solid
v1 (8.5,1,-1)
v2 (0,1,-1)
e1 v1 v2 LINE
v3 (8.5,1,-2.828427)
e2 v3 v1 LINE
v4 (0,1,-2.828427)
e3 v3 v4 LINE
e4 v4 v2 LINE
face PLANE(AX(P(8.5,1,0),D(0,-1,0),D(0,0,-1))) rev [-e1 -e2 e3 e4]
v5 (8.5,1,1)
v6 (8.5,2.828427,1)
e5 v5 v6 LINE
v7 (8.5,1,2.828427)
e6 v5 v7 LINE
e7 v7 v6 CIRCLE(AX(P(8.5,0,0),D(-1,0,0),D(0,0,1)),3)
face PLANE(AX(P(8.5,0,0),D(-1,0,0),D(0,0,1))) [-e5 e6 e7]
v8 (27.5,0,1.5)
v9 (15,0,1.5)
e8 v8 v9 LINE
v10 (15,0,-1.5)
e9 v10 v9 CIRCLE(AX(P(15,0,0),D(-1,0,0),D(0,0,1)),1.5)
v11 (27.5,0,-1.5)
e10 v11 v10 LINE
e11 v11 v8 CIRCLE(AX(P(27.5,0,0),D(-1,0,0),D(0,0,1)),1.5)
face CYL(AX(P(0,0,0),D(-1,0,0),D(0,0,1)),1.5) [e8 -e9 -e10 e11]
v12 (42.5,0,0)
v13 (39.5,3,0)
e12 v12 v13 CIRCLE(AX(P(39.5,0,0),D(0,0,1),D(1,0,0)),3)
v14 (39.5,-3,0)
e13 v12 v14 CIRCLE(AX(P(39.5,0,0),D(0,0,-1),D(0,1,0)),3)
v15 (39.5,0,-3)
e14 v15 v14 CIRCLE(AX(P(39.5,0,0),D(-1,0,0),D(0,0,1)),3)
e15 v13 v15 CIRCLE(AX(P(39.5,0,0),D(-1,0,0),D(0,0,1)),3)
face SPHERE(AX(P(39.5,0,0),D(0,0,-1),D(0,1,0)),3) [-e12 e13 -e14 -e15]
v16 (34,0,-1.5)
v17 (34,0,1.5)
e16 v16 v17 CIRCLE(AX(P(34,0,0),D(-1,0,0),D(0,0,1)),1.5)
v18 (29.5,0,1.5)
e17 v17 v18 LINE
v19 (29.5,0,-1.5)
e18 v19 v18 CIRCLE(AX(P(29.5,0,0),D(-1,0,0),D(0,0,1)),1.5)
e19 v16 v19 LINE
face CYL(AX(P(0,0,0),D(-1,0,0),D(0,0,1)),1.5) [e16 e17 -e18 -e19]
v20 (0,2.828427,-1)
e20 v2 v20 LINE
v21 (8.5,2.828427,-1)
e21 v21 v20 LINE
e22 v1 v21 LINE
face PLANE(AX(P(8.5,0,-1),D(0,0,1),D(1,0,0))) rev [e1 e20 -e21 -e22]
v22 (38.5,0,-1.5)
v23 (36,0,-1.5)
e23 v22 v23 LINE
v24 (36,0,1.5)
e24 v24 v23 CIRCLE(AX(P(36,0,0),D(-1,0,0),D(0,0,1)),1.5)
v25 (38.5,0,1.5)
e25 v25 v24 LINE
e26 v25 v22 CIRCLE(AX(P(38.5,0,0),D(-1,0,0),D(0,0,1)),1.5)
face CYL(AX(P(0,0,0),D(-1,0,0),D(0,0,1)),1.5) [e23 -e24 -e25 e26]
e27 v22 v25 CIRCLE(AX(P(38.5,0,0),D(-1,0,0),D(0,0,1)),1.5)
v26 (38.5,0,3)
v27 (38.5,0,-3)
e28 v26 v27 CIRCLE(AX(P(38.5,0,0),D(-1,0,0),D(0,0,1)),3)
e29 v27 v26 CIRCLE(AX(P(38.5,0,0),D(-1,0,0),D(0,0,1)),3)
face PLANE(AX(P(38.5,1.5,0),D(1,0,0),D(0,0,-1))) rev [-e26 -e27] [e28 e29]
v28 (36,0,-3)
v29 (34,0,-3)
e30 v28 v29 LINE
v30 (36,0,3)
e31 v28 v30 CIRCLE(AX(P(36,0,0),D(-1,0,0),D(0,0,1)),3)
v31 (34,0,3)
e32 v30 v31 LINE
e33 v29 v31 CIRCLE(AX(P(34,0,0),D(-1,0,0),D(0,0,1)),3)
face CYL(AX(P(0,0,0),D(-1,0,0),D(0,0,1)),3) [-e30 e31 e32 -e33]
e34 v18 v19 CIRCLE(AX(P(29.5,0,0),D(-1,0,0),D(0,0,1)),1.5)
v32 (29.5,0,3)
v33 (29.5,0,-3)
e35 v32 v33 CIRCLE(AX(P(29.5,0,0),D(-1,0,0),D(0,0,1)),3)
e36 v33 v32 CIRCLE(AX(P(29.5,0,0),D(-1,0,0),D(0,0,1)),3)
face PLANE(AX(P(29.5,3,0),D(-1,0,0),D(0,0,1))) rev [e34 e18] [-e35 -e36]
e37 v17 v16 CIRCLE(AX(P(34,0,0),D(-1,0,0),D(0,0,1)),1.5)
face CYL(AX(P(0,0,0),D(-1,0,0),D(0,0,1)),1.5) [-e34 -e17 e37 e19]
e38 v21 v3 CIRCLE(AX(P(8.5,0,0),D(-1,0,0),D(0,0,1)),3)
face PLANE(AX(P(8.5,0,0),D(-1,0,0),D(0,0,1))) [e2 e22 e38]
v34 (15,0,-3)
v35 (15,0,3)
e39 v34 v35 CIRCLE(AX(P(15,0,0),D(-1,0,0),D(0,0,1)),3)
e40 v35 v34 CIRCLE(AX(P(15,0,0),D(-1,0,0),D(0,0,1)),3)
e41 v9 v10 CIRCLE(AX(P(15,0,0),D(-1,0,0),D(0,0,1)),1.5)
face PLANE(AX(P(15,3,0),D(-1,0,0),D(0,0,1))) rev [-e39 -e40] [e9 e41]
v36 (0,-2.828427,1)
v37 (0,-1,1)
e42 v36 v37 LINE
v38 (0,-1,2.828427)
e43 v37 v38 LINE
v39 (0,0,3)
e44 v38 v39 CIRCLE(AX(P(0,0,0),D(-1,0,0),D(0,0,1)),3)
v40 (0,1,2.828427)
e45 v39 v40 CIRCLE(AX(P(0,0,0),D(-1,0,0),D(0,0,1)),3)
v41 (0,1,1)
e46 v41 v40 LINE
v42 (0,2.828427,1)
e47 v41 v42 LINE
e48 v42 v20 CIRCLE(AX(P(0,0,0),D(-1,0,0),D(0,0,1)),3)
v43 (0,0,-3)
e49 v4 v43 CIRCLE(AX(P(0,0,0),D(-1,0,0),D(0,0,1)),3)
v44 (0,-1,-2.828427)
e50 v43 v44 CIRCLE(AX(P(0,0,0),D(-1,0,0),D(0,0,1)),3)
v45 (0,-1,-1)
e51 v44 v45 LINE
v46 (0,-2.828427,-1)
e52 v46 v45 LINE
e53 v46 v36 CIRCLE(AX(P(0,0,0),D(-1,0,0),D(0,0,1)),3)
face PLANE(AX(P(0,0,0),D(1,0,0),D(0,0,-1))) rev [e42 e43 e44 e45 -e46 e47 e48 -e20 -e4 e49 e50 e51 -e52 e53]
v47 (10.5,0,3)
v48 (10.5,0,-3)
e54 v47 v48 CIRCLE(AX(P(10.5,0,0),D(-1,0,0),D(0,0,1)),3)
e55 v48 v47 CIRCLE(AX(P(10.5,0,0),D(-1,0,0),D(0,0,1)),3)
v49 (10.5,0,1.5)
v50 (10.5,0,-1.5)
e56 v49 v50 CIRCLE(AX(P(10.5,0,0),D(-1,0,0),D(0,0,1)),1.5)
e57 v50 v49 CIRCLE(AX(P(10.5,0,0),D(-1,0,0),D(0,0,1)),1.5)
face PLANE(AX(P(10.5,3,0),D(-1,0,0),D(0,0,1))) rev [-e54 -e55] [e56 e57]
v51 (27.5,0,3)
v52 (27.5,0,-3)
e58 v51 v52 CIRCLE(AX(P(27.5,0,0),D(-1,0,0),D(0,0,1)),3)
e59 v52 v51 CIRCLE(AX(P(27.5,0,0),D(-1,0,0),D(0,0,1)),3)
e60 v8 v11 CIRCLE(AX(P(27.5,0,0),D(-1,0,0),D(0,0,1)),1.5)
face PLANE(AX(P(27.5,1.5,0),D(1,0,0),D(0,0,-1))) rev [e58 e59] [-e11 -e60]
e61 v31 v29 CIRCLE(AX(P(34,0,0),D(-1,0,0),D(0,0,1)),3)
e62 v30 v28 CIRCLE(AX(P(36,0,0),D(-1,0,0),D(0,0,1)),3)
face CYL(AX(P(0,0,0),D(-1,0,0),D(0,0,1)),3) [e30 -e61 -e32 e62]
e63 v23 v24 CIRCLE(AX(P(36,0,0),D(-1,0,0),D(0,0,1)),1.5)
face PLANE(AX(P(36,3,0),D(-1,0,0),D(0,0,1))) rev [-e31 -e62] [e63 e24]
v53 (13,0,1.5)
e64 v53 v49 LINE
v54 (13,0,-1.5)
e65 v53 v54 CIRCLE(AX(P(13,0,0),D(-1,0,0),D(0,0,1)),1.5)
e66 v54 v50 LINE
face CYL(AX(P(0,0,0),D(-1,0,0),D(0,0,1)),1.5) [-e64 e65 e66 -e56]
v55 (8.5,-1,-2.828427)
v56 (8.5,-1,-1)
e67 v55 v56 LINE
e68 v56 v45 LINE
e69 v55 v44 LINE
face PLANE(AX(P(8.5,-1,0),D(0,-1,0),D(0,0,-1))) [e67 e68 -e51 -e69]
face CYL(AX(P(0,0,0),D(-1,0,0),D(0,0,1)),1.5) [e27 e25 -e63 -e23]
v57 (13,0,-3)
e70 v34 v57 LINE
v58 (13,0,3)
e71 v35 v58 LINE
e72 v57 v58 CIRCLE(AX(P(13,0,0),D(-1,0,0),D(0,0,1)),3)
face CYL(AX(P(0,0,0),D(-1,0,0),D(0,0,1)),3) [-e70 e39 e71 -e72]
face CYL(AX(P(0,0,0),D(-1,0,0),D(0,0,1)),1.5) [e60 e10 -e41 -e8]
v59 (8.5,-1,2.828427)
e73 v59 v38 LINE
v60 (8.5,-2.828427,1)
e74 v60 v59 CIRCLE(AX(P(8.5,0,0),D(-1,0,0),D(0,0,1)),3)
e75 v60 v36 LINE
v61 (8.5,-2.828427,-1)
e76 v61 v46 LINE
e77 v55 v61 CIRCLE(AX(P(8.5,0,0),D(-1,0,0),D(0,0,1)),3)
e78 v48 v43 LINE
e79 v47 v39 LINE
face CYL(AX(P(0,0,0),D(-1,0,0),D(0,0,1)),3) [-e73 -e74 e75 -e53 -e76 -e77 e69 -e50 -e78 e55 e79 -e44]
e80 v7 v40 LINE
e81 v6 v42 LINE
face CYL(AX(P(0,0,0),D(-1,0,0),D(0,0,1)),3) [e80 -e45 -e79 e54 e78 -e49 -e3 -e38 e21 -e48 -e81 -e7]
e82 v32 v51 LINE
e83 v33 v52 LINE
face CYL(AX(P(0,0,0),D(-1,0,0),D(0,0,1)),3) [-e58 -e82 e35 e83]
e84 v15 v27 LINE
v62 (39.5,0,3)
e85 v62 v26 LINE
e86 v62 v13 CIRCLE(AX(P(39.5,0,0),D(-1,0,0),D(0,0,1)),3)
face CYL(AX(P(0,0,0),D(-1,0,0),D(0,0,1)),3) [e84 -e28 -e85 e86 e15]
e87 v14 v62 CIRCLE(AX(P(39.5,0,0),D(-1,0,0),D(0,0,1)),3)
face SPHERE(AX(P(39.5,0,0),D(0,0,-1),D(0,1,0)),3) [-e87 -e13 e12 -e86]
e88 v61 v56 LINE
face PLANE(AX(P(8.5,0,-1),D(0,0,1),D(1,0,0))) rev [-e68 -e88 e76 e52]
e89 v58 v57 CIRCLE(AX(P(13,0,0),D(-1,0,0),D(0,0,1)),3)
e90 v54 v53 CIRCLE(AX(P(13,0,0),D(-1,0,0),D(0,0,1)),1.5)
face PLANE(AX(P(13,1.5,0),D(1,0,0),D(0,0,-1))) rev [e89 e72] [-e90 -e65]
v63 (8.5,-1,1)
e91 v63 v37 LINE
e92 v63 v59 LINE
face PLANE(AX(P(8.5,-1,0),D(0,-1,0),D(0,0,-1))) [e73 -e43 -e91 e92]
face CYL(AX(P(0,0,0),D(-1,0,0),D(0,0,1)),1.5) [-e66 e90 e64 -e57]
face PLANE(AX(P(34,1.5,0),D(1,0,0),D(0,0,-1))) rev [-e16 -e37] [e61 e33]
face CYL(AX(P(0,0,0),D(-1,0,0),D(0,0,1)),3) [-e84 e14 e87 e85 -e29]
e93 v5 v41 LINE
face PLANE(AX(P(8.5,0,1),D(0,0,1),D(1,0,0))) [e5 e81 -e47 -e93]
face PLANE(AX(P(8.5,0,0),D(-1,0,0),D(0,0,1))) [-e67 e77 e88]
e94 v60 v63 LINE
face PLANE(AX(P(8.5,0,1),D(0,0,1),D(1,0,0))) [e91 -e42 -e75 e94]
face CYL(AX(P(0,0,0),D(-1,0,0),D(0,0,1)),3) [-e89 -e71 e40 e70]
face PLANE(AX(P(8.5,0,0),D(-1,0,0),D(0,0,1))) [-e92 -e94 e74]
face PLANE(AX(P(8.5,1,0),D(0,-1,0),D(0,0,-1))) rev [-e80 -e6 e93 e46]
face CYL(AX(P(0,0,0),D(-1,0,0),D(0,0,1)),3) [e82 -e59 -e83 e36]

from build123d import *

# Parameters (mm, degrees)
CUT_EXTRUDE1_START = -8.5
CUT_EXTRUDE1_DEPTH = 8.5


with BuildPart() as part:
    # Sketch1 → Revolve1 (revolve)
    with BuildSketch(Plane.XY, mode=Mode.PRIVATE) as revolve1_sk:
        with BuildLine():
            Line((0, 0), (0, 3))
            Line((0, 3), (10.5, 3))
            Line((10.5, 3), (10.5, 1.5))
            Line((10.5, 1.5), (13, 1.5))
            Line((13, 1.5), (13, 3))
            Line((13, 3), (15, 3))
            Line((15, 3), (15, 1.5))
            Line((15, 1.5), (27.5, 1.5))
            Line((27.5, 1.5), (27.5, 3))
            Line((27.5, 3), (29.5, 3))
            Line((29.5, 3), (29.5, 1.5))
            Line((29.5, 1.5), (34, 1.5))
            Line((34, 1.5), (34, 3))
            Line((34, 3), (36, 3))
            Line((36, 3), (36, 1.5))
            Line((36, 1.5), (38.5, 1.5))
            Line((38.5, 1.5), (38.5, 3))
            Line((38.5, 3), (39.5, 3))
            ThreePointArc((39.5, 3), (41.621320344, 2.121320344), (42.5, 0))
            Line((42.5, 0), (0, 0))
        make_face()
    revolve(revolve1_sk.sketch.rotate(Axis((0, 0, 0), (1, 0, 0)), 90), axis=Axis((0, 0, 0), (1, 0, 0)))

    # Sketch2 → Cut-Extrude1 (cut)
    with BuildSketch(Plane.ZY.offset(CUT_EXTRUDE1_START)):
        with BuildLine():
            Line((1, 2.828427125), (1, 1))
            Line((1, 1), (2.828427125, 1))
            ThreePointArc((2.828427125, 1), (2.121320344, 2.121320344), (1, 2.828427125))
        make_face()
        with BuildLine():
            Line((2.828427125, -1), (1, -1))
            Line((1, -1), (1, -2.828427125))
            ThreePointArc((1, -2.828427125), (2.121320344, -2.121320344), (2.828427125, -1))
        make_face()
        with BuildLine():
            ThreePointArc((-1, 2.828427125), (-2.121320344, 2.121320344), (-2.828427125, 1))
            Line((-2.828427125, 1), (-1, 1))
            Line((-1, 1), (-1, 2.828427125))
        make_face()
        with BuildLine():
            Line((-1, -1), (-2.828427125, -1))
            ThreePointArc((-2.828427125, -1), (-2.121320344, -2.121320344), (-1, -2.828427125))
            Line((-1, -2.828427125), (-1, -1))
        make_face()
    extrude(amount=CUT_EXTRUDE1_DEPTH, mode=Mode.SUBTRACT)


solid = part.part
